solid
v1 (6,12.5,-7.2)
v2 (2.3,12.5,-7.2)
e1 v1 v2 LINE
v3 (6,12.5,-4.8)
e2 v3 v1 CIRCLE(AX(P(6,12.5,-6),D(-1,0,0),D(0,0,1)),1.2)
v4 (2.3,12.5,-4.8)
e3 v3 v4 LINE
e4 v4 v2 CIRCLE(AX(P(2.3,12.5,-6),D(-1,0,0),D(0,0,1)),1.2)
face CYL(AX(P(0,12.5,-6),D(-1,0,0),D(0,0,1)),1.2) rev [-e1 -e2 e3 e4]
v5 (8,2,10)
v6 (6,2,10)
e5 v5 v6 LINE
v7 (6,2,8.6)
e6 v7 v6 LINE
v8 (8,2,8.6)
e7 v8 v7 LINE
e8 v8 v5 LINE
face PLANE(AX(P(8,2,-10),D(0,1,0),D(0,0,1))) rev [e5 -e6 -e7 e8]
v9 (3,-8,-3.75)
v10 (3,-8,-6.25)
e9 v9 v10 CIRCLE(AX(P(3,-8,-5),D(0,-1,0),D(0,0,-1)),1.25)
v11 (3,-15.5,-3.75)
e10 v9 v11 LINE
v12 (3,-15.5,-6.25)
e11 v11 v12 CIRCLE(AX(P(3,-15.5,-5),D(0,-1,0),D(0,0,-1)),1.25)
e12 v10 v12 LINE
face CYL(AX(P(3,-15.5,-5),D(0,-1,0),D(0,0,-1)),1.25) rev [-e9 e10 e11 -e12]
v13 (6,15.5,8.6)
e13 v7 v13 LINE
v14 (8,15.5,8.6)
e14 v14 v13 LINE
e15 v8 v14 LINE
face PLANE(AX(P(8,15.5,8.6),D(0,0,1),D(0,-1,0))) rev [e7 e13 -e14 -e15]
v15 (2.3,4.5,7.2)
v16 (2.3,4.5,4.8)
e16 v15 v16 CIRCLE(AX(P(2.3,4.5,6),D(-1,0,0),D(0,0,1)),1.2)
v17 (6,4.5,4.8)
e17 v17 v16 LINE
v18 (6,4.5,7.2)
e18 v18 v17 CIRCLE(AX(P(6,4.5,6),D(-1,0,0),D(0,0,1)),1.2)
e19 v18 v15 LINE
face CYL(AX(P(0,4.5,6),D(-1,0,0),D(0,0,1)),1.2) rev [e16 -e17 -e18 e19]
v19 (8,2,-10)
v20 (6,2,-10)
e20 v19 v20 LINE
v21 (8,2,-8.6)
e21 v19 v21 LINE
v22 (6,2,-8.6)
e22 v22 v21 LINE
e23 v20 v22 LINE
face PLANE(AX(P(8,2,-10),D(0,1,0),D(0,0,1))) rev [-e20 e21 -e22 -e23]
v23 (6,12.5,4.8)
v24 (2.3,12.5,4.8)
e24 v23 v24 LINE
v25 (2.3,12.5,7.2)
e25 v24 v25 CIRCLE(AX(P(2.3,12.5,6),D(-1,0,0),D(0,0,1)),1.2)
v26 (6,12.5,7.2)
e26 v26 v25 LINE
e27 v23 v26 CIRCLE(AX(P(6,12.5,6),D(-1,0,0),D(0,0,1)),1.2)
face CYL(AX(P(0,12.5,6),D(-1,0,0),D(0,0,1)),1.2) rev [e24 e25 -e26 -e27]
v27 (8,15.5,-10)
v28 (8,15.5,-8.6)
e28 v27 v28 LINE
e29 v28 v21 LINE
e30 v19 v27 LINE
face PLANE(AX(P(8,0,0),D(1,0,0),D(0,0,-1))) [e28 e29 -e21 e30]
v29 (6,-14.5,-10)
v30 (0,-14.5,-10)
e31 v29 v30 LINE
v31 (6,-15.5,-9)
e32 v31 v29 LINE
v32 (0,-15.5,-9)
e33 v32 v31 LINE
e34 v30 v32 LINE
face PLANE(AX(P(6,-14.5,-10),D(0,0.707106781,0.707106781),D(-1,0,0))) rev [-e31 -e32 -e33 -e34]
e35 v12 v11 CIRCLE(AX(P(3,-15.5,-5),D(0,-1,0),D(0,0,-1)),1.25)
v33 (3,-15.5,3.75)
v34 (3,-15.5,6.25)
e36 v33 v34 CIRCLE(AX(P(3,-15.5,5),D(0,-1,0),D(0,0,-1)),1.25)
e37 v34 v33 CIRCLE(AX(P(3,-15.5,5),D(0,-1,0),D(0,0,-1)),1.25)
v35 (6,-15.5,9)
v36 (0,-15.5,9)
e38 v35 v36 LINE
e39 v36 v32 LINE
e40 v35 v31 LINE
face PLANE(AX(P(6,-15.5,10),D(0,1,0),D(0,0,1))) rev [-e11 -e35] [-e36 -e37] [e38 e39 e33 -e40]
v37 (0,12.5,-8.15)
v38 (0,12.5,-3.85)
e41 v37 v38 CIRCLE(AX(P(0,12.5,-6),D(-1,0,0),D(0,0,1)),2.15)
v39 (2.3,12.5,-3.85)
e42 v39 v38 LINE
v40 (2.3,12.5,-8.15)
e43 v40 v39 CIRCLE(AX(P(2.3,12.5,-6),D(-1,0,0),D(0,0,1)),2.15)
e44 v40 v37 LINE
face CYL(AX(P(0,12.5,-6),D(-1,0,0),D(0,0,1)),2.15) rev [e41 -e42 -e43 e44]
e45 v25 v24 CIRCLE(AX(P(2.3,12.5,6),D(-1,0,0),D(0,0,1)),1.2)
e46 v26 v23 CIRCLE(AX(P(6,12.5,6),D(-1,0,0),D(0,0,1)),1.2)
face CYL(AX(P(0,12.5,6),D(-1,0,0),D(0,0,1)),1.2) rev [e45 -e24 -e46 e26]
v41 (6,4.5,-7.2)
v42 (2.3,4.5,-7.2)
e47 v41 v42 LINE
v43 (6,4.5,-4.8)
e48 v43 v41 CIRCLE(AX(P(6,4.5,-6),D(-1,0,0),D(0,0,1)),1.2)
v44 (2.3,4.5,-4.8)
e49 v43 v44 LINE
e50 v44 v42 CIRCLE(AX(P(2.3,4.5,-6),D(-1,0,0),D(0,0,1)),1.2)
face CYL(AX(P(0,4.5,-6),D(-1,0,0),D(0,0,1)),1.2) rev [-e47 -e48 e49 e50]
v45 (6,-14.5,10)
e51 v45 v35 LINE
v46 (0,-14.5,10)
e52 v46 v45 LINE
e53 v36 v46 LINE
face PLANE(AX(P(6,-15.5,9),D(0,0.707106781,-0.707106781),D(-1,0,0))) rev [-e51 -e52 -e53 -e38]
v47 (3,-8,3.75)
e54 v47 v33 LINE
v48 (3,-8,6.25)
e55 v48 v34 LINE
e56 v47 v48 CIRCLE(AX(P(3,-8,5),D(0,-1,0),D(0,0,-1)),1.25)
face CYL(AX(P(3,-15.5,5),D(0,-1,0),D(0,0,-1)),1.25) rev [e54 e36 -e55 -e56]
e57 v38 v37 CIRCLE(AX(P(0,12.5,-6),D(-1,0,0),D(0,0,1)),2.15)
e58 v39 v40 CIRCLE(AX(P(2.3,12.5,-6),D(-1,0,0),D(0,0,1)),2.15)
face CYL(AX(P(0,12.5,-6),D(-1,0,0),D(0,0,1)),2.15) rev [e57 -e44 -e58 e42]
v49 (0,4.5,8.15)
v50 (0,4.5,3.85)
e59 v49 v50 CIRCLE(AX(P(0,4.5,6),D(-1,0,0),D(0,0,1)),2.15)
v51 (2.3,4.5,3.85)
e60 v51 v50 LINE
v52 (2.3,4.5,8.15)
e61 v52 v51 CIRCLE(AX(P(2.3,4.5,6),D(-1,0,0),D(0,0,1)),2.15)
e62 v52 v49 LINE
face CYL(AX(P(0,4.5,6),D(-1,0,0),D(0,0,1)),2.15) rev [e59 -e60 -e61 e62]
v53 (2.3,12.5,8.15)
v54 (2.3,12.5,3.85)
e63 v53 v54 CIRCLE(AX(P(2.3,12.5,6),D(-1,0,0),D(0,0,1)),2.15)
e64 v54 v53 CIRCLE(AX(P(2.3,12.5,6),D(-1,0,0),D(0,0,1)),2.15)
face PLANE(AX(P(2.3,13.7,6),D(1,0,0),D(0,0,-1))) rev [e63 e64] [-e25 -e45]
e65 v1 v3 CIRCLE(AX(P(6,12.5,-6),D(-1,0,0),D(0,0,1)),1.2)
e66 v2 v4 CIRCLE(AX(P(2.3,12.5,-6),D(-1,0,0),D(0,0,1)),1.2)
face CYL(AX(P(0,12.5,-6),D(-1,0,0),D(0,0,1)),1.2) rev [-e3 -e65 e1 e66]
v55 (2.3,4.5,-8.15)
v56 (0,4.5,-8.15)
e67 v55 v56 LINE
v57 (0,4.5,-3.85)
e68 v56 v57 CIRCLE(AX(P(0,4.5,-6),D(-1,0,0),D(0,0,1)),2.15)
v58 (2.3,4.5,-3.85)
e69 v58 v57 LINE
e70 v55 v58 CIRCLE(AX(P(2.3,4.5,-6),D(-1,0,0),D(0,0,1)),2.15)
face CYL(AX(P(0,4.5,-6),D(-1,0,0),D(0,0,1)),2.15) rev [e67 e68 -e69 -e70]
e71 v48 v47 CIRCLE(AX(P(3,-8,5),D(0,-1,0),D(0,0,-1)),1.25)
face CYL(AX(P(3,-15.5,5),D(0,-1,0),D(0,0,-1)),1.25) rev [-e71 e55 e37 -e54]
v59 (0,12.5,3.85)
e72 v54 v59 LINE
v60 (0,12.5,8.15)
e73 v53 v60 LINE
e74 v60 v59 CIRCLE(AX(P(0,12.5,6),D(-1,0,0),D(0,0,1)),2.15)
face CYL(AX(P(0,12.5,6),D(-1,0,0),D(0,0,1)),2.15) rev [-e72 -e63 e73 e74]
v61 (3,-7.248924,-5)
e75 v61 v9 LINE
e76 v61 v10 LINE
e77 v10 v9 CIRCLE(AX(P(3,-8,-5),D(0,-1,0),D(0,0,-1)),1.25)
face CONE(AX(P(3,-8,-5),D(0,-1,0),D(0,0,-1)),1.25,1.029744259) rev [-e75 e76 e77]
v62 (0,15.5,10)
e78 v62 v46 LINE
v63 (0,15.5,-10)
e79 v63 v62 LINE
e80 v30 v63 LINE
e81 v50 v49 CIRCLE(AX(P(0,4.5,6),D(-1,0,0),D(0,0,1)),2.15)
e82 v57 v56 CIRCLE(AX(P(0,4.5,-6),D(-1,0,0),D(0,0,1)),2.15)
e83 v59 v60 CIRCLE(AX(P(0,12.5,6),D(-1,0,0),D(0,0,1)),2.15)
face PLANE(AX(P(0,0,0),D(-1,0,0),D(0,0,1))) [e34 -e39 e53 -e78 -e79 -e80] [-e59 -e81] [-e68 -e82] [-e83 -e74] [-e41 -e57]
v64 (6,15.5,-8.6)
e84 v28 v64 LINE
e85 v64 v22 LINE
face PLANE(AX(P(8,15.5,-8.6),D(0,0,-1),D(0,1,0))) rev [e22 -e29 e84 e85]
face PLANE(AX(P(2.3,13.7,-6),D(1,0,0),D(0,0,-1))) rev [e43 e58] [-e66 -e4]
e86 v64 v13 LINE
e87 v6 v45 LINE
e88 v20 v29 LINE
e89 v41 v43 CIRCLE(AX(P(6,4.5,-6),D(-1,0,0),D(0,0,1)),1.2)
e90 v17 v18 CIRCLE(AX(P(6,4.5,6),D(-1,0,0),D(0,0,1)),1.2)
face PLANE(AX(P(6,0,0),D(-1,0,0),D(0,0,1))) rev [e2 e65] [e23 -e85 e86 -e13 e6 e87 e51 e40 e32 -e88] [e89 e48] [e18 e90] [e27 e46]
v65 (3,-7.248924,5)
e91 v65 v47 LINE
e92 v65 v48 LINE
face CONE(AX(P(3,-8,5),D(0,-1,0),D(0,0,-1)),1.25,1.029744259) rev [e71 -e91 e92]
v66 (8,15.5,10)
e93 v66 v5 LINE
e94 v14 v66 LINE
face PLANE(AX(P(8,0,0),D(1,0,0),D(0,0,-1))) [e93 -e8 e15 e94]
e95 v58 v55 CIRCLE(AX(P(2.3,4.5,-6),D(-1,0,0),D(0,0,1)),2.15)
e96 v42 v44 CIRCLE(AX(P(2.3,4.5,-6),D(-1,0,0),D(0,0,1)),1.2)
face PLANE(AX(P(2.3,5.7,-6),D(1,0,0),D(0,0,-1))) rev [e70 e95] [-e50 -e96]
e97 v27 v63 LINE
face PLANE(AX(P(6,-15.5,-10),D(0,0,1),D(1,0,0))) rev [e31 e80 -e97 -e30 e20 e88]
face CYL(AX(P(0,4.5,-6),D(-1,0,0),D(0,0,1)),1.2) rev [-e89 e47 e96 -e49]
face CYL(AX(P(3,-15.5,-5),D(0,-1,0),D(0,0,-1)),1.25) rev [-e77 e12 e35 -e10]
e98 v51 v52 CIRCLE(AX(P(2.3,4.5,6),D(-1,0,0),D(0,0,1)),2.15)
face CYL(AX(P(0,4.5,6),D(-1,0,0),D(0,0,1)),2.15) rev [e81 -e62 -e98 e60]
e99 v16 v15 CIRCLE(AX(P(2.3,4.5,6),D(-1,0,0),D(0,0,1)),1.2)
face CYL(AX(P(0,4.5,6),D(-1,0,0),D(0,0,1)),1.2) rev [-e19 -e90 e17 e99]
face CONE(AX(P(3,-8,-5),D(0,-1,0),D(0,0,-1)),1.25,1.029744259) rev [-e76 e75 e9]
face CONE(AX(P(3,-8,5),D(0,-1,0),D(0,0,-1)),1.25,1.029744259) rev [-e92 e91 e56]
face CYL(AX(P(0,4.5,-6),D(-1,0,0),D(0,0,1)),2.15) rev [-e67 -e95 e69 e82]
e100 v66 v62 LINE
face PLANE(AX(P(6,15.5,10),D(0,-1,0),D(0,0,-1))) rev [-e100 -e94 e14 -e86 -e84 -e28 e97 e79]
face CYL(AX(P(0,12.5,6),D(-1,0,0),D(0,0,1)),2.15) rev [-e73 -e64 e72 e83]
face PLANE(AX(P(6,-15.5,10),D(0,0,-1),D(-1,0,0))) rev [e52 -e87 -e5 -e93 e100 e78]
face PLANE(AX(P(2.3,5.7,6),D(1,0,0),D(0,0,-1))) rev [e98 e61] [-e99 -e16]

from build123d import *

# Parameters (mm, degrees)
SKETCH2_W                                            = 20
SKETCH2_H                                            = 31
BOSS_EXTRUDE1_DEPTH                                  = 6
SKETCH3_W                                            = 1.4
SKETCH3_H                                            = 31
BOSS_EXTRUDE2_DEPTH                                  = 2
SKETCH4_W                                            = 2
SKETCH4_H                                            = 17.5
CUT_EXTRUDE1_DEPTH                                   = 27.537709019
CBORE_FOR_M2_HEXAGON_SOCKET_HEAD_CAP_SCR_D           = 2.4
CBORE_FOR_M2_HEXAGON_SOCKET_HEAD_CAP_SCR_DEPTH       = 10.1
CBORE_FOR_M2_HEXAGON_SOCKET_HEAD_CAP_SCR_CBORE_D     = 4.3
CBORE_FOR_M2_HEXAGON_SOCKET_HEAD_CAP_SCR_CBORE_DEPTH = 2.3
CBORE_FOR_M2_HEXAGON_SOCKET_HEAD_CAP_SCR_TIP         = 0.721032743
M3_TAPPED_HOLE1_D                                    = 2.5
M3_TAPPED_HOLE1_DEPTH                                = 7.5
M3_TAPPED_HOLE1_TIP                                  = 0.751075774
CHAMFER1_SIZE                                        = 1


with BuildPart() as part:
    # Sketch2 → Boss-Extrude1 (new body)
    with BuildSketch(Plane(origin=(0, 0, 0), x_dir=(0, 0, -1), z_dir=(1, 0, 0))):
        Rectangle(SKETCH2_W, SKETCH2_H)
    extrude(amount=BOSS_EXTRUDE1_DEPTH)

    # Sketch3 → Boss-Extrude2 (add)
    with BuildSketch(Plane(origin=(6, 0, 0), x_dir=(0, 0, -1), z_dir=(1, 0, 0))):
        with Locations((-9.3, 0)):
            Rectangle(SKETCH3_W, SKETCH3_H)
        with Locations((9.3, 0)):
            Rectangle(SKETCH3_W, SKETCH3_H)
    extrude(amount=BOSS_EXTRUDE2_DEPTH)

    # Sketch4 → Cut-Extrude1 (cut, through all)
    with BuildSketch(Plane.XY.offset(10)):
        with Locations((7, -6.75)):
            Rectangle(SKETCH4_W, SKETCH4_H)
    extrude(amount=-CUT_EXTRUDE1_DEPTH, mode=Mode.SUBTRACT)

    # CBORE for M2 Hexagon socket head cap screws1
    with Locations(Plane.ZY):
        with Locations((6, 12.5), (-6, 12.5), (-6, 4.5), (6, 4.5)):
            CounterBoreHole(CBORE_FOR_M2_HEXAGON_SOCKET_HEAD_CAP_SCR_D / 2, CBORE_FOR_M2_HEXAGON_SOCKET_HEAD_CAP_SCR_CBORE_D / 2, CBORE_FOR_M2_HEXAGON_SOCKET_HEAD_CAP_SCR_CBORE_DEPTH, depth=CBORE_FOR_M2_HEXAGON_SOCKET_HEAD_CAP_SCR_DEPTH)
            with Locations((0, 0, -(CBORE_FOR_M2_HEXAGON_SOCKET_HEAD_CAP_SCR_DEPTH + CBORE_FOR_M2_HEXAGON_SOCKET_HEAD_CAP_SCR_TIP / 2))):  # 118° drill point
                Cone(0, CBORE_FOR_M2_HEXAGON_SOCKET_HEAD_CAP_SCR_D / 2, CBORE_FOR_M2_HEXAGON_SOCKET_HEAD_CAP_SCR_TIP, mode=Mode.SUBTRACT)

    # M3 Tapped Hole1
    with Locations(Plane(origin=(0, -15.5, 0), x_dir=(-1, 0, 0), z_dir=(0, -1, 0))):
        with Locations((-3, 5), (-3, -5)):
            Hole(M3_TAPPED_HOLE1_D / 2, depth=M3_TAPPED_HOLE1_DEPTH)
            with Locations((0, 0, -(M3_TAPPED_HOLE1_DEPTH + M3_TAPPED_HOLE1_TIP / 2))):  # 118° drill point
                Cone(0, M3_TAPPED_HOLE1_D / 2, M3_TAPPED_HOLE1_TIP, mode=Mode.SUBTRACT)

    # Chamfer1
    chamfer1_edges = [part.edges().sort_by_distance(p)[0] for p in [
        (3, -15.5, -10),
        (3, -15.5, 10),
    ]]
    chamfer(chamfer1_edges, length=CHAMFER1_SIZE)


solid = part.part
